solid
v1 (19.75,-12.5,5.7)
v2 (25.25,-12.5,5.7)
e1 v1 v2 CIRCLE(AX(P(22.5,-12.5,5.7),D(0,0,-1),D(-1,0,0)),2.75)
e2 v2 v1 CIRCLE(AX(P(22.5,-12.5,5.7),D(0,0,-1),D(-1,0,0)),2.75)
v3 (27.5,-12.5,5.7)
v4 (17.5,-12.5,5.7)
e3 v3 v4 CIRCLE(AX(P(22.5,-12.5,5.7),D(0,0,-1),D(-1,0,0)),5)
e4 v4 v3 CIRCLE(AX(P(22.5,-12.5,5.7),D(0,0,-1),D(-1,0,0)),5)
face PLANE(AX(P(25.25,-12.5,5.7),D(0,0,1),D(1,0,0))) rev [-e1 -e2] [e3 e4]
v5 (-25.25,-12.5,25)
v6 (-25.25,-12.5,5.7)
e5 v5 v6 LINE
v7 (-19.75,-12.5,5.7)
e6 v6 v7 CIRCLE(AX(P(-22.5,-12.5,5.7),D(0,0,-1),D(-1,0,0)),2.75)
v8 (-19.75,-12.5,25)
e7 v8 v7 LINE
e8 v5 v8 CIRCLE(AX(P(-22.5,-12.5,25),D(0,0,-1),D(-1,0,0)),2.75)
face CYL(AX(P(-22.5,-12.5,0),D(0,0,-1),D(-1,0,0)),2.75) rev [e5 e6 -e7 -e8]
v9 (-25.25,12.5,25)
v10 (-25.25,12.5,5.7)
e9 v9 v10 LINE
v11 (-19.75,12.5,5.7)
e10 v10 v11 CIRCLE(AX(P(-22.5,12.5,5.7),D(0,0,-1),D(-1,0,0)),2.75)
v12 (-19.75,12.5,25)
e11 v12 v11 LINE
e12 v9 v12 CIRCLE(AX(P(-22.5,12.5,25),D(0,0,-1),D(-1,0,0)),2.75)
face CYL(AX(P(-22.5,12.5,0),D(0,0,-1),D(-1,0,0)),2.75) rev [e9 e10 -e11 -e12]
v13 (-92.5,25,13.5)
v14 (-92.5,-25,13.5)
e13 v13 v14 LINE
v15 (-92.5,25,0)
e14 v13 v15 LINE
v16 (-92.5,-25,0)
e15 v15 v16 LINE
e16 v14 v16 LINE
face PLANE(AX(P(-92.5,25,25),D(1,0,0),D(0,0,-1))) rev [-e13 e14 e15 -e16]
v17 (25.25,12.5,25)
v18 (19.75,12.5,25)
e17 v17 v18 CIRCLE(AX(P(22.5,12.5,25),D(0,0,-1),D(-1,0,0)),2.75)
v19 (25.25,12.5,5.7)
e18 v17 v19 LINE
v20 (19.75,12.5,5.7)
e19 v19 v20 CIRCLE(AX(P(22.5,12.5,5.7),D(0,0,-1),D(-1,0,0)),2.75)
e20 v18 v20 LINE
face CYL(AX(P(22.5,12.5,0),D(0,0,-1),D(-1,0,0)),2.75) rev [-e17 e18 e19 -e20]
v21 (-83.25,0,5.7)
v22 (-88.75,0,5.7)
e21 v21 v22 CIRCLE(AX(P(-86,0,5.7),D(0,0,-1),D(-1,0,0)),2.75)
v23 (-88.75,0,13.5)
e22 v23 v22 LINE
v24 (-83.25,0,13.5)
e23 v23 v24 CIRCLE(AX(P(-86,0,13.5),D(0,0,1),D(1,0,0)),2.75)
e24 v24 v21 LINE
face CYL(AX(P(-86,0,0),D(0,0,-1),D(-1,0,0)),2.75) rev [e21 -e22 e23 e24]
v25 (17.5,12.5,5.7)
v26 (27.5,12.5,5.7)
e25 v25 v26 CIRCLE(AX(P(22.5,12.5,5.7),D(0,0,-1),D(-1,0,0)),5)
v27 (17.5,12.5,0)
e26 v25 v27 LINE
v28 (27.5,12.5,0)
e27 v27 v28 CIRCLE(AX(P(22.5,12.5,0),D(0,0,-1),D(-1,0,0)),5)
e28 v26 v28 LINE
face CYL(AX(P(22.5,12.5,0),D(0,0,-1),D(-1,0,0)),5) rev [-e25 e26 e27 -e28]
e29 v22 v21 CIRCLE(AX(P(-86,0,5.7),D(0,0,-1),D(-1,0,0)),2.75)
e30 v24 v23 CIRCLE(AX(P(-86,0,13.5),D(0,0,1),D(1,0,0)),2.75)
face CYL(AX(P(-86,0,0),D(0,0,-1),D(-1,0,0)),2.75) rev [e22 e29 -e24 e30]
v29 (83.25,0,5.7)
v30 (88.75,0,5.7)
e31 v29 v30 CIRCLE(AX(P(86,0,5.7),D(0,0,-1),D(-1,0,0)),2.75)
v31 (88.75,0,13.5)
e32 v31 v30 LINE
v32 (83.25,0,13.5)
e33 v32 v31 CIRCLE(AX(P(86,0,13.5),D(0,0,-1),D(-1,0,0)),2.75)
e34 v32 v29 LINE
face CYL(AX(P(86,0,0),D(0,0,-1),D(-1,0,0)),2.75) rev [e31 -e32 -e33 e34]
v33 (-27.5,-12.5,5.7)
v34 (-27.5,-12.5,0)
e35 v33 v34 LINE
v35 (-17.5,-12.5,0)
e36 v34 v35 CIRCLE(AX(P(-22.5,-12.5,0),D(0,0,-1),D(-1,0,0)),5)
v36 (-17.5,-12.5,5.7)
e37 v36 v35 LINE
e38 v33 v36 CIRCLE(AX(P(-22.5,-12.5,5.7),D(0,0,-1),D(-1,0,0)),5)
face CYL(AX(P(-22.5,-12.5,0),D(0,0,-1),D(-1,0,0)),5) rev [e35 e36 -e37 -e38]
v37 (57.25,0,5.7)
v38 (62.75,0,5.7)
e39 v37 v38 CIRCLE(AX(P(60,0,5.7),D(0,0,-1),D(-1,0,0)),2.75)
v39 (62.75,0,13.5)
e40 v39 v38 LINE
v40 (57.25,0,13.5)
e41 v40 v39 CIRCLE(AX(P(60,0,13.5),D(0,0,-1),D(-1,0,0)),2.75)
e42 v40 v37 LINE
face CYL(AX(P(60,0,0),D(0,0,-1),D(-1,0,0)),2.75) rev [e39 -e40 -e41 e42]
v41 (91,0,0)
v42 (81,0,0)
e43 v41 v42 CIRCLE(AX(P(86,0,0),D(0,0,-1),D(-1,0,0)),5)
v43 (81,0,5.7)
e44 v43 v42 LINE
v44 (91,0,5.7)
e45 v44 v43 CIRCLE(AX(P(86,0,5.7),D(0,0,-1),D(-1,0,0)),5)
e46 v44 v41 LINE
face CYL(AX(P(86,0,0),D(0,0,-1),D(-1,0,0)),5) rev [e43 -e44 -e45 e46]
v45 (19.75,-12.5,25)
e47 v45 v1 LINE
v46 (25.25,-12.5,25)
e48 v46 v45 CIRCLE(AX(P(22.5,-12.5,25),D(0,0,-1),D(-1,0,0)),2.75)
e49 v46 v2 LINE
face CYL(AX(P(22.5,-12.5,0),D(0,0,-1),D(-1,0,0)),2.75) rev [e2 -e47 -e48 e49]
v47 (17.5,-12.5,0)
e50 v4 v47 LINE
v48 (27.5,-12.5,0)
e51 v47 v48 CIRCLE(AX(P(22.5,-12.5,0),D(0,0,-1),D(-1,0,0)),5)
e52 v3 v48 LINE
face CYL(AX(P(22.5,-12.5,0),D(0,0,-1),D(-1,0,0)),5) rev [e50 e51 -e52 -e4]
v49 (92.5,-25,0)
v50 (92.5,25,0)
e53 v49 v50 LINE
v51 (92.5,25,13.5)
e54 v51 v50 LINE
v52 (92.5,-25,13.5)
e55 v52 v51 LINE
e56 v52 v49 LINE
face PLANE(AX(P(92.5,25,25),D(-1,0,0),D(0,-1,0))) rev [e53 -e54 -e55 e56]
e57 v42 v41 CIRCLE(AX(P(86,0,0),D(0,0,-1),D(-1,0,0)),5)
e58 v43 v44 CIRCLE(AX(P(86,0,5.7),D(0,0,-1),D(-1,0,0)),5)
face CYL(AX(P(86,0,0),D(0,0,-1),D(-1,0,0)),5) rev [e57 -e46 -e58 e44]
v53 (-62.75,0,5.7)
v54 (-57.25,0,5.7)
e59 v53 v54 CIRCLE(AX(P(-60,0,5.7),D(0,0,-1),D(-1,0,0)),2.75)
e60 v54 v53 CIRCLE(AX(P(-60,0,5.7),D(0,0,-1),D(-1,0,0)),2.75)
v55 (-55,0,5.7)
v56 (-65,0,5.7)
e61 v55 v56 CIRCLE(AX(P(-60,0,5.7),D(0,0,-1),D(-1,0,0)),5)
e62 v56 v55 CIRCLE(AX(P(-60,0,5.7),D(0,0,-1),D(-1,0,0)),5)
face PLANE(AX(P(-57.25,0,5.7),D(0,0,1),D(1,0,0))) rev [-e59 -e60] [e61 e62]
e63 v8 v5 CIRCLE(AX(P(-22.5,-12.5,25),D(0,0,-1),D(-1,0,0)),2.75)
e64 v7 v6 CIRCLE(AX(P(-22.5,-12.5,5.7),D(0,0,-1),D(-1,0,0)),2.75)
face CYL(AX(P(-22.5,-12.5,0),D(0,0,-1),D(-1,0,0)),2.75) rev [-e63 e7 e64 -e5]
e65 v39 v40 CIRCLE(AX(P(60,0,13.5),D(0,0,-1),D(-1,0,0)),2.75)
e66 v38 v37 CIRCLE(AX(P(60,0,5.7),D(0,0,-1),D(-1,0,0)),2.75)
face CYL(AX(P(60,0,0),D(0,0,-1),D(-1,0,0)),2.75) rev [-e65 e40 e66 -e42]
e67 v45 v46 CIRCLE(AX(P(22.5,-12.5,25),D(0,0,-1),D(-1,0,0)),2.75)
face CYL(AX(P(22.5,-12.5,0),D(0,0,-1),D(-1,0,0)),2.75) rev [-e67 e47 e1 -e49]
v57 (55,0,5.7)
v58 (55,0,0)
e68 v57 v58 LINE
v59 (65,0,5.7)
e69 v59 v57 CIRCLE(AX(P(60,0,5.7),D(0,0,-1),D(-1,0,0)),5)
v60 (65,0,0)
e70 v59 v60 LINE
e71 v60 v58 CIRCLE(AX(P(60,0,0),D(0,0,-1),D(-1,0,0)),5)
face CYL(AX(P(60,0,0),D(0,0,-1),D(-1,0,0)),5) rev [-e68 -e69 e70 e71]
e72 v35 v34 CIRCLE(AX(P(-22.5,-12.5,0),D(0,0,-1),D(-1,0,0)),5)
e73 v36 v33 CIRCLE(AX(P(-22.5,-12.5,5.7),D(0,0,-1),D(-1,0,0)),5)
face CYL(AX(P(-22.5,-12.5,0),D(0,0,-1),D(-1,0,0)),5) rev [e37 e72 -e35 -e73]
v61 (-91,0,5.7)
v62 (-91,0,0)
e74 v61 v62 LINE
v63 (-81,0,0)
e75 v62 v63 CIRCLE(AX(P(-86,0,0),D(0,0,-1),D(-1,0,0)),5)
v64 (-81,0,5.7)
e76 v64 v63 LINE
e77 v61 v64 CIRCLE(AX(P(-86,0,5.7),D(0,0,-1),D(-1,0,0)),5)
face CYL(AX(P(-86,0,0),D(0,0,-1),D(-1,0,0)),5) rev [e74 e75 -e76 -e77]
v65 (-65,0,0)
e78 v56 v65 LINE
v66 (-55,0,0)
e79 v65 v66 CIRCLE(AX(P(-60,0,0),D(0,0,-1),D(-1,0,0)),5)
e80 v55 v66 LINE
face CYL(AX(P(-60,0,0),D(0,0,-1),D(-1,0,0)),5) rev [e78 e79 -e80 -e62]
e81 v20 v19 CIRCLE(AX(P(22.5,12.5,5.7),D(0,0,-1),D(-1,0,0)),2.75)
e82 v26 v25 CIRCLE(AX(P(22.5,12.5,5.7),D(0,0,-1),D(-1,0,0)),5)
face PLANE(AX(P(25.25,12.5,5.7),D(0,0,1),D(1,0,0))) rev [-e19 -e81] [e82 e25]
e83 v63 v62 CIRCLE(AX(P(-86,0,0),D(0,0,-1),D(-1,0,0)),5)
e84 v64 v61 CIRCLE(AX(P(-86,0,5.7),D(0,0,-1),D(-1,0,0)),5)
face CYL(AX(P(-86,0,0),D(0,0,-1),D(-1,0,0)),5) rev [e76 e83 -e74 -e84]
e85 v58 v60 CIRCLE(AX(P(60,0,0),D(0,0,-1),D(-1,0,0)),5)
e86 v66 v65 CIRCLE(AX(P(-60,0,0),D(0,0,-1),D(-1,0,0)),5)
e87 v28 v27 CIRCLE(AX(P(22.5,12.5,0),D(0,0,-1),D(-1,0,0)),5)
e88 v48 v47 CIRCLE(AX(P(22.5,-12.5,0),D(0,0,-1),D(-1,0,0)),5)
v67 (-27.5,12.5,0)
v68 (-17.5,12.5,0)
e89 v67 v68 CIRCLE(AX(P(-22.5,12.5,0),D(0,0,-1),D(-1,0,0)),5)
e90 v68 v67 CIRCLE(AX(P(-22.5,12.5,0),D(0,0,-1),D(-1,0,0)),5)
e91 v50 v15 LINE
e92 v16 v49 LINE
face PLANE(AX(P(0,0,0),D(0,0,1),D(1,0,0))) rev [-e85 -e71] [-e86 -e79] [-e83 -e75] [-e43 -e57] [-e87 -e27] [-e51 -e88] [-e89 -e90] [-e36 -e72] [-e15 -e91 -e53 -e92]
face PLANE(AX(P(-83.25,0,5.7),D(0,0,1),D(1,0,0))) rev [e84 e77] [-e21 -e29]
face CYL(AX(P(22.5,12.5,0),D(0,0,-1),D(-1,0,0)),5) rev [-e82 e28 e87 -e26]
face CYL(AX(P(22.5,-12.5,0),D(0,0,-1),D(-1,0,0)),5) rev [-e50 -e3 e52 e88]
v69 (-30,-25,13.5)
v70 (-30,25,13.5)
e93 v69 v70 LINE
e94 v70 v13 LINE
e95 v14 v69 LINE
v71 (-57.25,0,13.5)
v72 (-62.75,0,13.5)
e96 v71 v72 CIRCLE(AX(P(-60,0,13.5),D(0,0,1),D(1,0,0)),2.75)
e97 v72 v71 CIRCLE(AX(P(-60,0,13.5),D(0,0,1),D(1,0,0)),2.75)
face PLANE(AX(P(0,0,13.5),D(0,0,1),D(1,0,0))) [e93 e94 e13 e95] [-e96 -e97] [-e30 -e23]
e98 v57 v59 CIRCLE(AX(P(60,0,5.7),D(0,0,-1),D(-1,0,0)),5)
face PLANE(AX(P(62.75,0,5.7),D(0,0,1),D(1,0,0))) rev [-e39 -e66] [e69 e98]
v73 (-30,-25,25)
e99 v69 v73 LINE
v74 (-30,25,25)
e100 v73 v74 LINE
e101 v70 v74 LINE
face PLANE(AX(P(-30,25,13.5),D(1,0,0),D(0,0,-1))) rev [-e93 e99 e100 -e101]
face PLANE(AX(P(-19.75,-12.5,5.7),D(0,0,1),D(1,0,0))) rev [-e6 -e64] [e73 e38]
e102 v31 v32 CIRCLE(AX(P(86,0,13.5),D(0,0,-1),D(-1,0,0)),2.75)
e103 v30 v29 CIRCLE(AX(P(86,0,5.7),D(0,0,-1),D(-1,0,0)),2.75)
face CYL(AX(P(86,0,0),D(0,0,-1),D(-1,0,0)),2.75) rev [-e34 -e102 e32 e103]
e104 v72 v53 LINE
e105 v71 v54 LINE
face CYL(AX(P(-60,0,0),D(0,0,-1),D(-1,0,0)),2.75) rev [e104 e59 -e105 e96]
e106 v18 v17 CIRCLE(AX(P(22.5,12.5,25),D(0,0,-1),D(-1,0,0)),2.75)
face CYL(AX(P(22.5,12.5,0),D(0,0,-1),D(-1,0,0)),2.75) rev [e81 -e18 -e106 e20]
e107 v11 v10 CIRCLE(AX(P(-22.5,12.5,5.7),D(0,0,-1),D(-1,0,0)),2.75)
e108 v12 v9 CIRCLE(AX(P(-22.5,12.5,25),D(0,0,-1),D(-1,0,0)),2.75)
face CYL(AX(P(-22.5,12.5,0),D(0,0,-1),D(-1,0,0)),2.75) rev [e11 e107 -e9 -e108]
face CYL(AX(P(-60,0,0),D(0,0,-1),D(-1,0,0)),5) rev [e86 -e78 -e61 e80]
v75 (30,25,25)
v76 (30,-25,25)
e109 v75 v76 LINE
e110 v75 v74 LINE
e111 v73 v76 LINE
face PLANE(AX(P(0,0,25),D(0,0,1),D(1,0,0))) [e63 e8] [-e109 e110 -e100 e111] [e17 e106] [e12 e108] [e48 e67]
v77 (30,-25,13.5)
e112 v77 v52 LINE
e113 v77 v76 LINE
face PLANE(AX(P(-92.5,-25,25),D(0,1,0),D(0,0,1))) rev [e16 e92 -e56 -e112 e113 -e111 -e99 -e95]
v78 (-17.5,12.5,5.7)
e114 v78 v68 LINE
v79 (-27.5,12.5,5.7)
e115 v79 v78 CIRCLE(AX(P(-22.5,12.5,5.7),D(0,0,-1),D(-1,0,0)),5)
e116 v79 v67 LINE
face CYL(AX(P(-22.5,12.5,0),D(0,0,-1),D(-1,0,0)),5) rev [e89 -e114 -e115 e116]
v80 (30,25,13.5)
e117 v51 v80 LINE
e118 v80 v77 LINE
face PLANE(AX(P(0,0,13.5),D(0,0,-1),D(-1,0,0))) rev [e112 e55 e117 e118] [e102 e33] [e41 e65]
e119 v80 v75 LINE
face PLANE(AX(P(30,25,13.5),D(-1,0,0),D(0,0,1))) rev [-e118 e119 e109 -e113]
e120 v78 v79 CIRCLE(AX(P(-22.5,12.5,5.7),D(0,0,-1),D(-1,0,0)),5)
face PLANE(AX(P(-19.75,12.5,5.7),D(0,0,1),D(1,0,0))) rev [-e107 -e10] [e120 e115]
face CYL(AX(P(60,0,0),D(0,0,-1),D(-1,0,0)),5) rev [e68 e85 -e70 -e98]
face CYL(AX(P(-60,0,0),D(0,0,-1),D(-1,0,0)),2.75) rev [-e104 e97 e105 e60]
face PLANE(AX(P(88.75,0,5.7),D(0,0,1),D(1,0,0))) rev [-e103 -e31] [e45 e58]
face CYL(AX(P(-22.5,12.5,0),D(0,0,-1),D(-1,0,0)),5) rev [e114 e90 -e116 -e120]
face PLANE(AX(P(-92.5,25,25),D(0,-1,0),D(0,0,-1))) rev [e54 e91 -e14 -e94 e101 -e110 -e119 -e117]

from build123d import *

# Parameters (mm, degrees)
SKETCH1_W                                         = 185
SKETCH1_H                                         = 50
BOSS_EXTRUDE1_DEPTH                               = 25
SKETCH2_W                                         = 62.5
SKETCH2_H                                         = 50
CUT_EXTRUDE1_DEPTH                                = 11.5
M5_SOCKET_HEAD_CAP_SCREW_COUNTERBORE1_D           = 5.5
M5_SOCKET_HEAD_CAP_SCREW_COUNTERBORE1_CBORE_D     = 10
M5_SOCKET_HEAD_CAP_SCREW_COUNTERBORE1_CBORE_DEPTH = 5.7
M5_SOCKET_HEAD_CAP_SCREW_COUNTERBORE2_D           = 5.5
M5_SOCKET_HEAD_CAP_SCREW_COUNTERBORE2_CBORE_D     = 10
M5_SOCKET_HEAD_CAP_SCREW_COUNTERBORE2_CBORE_DEPTH = 5.7


with BuildPart() as part:
    # Sketch1 → Boss-Extrude1 (new body)
    with BuildSketch(Plane.XY):
        Rectangle(SKETCH1_W, SKETCH1_H)
    extrude(amount=BOSS_EXTRUDE1_DEPTH)

    # Sketch2 → Cut-Extrude1 (cut)
    with BuildSketch(Plane.XY.offset(25)):
        with Locations((-61.25, 0)):
            Rectangle(SKETCH2_W, SKETCH2_H)
        with Locations((61.25, 0)):
            Rectangle(SKETCH2_W, SKETCH2_H)
    extrude(amount=-CUT_EXTRUDE1_DEPTH, mode=Mode.SUBTRACT)

    # M5 socket head cap screw counterbore1 (through all)
    with Locations(Plane(origin=(0, 0, 0), x_dir=(-1, 0, 0), z_dir=(0, 0, -1))):
        with Locations((-86, 0), (-60, 0), (60, 0), (86, 0)):
            CounterBoreHole(M5_SOCKET_HEAD_CAP_SCREW_COUNTERBORE1_D / 2, M5_SOCKET_HEAD_CAP_SCREW_COUNTERBORE1_CBORE_D / 2, M5_SOCKET_HEAD_CAP_SCREW_COUNTERBORE1_CBORE_DEPTH)

    # M5 socket head cap screw counterbore2 (through all)
    with Locations(Plane(origin=(0, 0, 0), x_dir=(-1, 0, 0), z_dir=(0, 0, -1))):
        with Locations((-22.5, 12.5), (-22.5, -12.5), (22.5, 12.5), (22.5, -12.5)):
            CounterBoreHole(M5_SOCKET_HEAD_CAP_SCREW_COUNTERBORE2_D / 2, M5_SOCKET_HEAD_CAP_SCREW_COUNTERBORE2_CBORE_D / 2, M5_SOCKET_HEAD_CAP_SCREW_COUNTERBORE2_CBORE_DEPTH)


solid = part.part
